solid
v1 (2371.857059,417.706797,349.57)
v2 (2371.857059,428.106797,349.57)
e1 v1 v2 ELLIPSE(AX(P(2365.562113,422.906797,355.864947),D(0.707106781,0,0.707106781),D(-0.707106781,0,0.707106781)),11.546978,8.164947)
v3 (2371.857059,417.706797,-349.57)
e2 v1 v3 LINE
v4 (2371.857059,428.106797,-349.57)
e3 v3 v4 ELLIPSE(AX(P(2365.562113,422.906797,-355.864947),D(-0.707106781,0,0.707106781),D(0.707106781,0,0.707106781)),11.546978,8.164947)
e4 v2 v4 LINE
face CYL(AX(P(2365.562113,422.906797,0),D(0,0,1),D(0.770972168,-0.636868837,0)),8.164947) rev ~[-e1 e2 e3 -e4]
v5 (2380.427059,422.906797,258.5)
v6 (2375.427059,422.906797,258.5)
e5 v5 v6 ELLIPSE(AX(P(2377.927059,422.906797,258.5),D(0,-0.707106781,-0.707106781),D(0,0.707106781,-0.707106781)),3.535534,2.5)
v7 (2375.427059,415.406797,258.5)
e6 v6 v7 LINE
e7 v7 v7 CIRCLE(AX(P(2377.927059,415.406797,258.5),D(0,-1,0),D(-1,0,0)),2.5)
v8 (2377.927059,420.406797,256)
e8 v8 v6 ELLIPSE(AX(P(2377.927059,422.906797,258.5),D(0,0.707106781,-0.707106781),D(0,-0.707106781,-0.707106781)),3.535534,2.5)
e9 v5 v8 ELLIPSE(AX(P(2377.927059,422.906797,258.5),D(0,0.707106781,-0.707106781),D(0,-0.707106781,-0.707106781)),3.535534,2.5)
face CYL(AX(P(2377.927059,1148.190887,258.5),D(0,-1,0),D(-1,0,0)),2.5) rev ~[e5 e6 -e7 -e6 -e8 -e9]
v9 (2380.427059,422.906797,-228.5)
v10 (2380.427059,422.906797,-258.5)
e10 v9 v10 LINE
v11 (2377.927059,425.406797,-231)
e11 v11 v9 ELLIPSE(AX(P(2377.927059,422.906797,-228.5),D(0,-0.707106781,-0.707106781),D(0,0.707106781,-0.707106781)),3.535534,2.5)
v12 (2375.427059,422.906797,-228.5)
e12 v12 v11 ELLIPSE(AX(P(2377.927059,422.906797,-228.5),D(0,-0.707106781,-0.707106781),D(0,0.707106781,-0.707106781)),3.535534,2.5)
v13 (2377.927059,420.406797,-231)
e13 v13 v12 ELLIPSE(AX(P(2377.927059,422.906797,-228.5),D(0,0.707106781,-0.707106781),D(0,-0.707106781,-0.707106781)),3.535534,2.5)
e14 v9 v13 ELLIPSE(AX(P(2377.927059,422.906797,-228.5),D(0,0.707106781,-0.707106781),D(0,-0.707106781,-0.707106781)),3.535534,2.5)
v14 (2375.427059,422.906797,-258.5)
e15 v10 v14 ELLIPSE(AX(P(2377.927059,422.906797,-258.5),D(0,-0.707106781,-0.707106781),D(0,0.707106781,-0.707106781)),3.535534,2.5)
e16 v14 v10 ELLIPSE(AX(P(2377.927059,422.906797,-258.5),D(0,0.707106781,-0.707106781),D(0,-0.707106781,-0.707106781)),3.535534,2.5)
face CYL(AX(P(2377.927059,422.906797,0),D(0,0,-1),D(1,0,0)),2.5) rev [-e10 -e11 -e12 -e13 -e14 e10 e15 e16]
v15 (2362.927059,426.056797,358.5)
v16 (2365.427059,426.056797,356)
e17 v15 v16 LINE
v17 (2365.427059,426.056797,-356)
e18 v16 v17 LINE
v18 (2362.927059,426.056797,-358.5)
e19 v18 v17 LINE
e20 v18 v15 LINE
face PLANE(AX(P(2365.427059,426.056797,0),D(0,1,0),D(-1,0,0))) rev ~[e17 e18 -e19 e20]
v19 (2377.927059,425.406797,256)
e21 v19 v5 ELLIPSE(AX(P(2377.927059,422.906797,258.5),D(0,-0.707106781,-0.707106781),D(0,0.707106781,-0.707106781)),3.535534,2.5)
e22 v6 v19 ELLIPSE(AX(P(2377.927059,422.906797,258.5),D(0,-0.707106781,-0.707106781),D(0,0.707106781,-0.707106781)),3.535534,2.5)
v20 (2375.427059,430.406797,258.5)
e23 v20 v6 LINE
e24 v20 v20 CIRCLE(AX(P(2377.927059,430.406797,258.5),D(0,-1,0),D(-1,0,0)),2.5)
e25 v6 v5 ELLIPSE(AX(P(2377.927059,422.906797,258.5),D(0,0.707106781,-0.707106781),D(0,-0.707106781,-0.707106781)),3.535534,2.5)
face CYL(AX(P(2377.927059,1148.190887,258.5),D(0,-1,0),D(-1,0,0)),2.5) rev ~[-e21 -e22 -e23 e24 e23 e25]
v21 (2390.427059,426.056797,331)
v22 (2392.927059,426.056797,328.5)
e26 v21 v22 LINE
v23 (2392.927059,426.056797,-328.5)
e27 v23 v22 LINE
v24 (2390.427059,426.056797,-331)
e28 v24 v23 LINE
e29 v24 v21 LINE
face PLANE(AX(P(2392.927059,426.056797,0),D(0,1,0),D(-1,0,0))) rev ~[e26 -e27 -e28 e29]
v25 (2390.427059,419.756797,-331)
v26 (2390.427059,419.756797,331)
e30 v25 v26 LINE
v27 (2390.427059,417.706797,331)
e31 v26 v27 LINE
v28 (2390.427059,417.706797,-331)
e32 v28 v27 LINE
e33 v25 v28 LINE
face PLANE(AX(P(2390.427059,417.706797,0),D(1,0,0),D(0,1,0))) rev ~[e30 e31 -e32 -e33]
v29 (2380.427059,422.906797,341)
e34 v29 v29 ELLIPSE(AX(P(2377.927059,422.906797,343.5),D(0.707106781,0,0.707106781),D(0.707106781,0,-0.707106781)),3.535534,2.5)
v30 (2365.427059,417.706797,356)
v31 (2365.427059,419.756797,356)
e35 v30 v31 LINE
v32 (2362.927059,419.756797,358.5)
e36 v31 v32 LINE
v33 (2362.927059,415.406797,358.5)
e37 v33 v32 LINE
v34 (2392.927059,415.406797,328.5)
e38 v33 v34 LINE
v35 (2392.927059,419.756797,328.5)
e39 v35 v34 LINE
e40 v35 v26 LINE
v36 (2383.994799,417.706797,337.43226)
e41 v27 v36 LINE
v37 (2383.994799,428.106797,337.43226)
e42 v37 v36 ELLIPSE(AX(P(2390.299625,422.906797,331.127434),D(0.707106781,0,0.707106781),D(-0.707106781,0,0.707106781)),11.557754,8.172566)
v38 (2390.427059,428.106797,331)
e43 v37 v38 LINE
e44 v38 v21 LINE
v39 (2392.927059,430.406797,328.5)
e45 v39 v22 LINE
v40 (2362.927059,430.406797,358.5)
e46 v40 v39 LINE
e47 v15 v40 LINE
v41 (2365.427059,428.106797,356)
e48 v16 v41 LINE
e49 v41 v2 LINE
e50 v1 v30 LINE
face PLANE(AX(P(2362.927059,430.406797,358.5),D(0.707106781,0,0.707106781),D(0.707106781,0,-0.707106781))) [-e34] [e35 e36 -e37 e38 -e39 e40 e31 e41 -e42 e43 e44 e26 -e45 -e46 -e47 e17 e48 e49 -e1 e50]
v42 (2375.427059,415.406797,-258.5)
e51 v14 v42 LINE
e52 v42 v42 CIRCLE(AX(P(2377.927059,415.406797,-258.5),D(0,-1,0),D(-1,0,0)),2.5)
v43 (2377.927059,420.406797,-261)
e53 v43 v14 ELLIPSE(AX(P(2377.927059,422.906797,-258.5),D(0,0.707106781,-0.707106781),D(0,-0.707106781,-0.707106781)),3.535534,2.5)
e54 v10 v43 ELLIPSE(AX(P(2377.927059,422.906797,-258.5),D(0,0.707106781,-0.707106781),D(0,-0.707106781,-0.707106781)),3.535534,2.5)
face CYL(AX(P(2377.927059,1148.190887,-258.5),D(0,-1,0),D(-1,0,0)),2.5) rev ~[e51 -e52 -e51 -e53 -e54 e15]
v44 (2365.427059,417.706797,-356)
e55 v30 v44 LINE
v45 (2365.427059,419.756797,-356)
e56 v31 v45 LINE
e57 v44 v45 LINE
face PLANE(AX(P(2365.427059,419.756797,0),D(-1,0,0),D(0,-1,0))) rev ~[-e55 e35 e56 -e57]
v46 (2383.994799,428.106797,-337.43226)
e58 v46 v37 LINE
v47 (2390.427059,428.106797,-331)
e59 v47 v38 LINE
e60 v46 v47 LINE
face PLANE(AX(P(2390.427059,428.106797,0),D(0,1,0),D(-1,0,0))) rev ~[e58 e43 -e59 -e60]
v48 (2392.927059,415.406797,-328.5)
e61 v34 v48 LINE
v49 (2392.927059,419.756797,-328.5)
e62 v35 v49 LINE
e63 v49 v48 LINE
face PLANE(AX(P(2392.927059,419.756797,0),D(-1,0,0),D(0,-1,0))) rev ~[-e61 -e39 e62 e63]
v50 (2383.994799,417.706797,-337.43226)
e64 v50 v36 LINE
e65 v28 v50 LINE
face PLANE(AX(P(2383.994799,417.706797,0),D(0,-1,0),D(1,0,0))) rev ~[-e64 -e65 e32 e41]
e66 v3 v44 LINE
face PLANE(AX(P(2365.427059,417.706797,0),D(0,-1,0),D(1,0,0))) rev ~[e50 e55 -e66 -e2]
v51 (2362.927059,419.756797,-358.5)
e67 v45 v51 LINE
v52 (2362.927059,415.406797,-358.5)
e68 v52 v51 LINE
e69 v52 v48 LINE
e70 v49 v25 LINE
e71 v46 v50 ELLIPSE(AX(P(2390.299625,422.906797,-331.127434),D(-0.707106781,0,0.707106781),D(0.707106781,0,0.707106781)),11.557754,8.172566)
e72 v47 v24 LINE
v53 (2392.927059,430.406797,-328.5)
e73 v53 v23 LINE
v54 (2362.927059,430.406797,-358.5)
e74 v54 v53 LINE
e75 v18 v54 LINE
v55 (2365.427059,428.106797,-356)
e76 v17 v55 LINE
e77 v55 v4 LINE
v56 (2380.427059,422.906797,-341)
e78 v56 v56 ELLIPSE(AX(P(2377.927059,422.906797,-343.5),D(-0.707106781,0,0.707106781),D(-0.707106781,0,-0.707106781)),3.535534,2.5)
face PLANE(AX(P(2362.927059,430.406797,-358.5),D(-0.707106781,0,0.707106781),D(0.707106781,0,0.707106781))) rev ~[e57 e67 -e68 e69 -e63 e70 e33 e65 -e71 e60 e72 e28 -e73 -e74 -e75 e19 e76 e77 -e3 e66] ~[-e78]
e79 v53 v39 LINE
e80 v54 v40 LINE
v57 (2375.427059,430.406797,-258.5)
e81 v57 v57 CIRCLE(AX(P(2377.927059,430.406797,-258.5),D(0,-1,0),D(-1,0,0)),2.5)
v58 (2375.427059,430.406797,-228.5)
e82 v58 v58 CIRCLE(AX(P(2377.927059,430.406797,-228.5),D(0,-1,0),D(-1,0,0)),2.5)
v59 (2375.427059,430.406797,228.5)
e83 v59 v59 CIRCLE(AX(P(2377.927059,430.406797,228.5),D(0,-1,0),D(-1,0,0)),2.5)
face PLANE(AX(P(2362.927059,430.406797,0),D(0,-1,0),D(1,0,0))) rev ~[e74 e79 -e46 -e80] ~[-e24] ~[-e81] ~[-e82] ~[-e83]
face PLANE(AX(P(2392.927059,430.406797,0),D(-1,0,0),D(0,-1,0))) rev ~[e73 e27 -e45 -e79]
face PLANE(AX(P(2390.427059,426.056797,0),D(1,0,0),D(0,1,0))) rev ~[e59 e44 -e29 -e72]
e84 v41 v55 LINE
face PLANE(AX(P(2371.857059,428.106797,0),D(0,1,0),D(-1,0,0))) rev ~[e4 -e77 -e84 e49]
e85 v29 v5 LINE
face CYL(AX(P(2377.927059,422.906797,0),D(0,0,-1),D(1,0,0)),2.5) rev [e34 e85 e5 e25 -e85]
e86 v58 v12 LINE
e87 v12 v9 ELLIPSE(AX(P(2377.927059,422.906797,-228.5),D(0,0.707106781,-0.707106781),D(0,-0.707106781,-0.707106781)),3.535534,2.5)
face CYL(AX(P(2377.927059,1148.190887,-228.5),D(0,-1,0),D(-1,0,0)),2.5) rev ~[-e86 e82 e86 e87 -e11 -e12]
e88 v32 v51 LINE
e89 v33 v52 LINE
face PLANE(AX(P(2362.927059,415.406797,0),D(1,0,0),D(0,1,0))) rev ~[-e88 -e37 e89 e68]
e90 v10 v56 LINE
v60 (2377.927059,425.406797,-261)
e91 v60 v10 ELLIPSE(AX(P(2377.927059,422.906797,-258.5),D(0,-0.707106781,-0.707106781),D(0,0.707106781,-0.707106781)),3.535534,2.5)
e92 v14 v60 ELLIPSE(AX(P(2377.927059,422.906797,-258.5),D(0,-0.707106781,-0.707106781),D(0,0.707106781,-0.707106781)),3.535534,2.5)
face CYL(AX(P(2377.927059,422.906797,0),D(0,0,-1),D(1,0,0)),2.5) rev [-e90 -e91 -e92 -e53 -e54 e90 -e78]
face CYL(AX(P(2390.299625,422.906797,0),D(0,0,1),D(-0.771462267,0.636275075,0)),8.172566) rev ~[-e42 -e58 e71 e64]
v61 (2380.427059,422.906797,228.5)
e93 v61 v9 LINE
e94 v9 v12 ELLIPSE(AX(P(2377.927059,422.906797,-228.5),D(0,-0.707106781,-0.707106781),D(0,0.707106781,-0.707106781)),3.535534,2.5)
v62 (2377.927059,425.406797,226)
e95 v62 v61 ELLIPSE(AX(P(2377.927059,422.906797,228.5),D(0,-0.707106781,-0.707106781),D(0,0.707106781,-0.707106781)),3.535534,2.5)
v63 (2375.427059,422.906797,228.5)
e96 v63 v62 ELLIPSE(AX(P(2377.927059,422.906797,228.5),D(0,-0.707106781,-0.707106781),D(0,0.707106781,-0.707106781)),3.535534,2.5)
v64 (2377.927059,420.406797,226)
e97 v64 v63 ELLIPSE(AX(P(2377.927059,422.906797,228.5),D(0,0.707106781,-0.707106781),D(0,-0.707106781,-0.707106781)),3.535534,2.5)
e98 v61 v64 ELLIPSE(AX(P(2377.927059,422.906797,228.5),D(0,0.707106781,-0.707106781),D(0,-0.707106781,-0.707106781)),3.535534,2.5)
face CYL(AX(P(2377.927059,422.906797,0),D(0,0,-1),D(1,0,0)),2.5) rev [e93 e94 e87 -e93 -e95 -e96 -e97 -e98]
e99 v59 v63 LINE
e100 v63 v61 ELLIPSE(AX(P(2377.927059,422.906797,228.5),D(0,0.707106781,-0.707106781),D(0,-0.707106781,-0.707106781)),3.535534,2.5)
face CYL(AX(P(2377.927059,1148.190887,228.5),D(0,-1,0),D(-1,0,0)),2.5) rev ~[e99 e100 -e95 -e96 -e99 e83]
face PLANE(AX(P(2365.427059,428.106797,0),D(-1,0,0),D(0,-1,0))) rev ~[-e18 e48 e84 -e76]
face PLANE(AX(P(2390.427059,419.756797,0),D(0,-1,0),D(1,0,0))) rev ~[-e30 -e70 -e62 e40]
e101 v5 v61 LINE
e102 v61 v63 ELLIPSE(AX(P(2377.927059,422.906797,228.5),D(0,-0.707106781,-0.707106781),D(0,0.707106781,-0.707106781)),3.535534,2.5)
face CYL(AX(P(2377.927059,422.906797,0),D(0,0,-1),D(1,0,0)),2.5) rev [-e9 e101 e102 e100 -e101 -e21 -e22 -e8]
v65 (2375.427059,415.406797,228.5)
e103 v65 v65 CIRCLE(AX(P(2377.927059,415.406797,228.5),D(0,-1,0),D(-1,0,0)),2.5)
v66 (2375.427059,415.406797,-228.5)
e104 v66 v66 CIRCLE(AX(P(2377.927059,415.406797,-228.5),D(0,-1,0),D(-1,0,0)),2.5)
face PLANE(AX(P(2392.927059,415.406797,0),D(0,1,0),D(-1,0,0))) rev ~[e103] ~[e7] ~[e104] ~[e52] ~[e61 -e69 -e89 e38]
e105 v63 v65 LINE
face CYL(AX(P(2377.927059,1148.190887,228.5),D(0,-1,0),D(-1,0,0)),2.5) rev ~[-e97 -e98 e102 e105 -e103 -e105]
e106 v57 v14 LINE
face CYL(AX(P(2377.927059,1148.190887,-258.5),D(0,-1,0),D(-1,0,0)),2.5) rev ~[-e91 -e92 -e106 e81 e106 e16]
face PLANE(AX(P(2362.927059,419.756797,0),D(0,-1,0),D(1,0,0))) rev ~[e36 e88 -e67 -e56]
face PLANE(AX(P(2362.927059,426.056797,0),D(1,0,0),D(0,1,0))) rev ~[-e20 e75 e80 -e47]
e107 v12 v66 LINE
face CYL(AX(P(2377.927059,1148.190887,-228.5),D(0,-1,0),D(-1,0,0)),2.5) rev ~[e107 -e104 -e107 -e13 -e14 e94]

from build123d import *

# Parameters (mm, degrees)
MODEL_R             = 2.5
EXTRUDE_1_DEPTH     = 358.5
CUT_EXTRUDE_1_DEPTH = 2420.679144403
HOLE_WIZARD_M6_1_D  = 5


with BuildPart() as part:
    # Model → 凸台-拉伸1 (new, symmetric)
    with BuildSketch(Plane.XY):
        with BuildLine():
            Line((2390.427059452, 419.756797217), (2392.927059452, 419.756797217))
            Line((2392.927059452, 419.756797217), (2392.927059452, 415.406797217))
            Line((2392.927059452, 415.406797217), (2362.927059452, 415.406797217))
            Line((2362.927059452, 415.406797217), (2362.927059452, 419.756797217))
            Line((2362.927059452, 419.756797217), (2365.427059452, 419.756797217))
            Line((2365.427059452, 419.756797217), (2365.427059452, 417.706797217))
            Line((2365.427059452, 417.706797217), (2371.857059452, 417.706797217))
            ThreePointArc((2371.857059452, 417.706797217), (2373.727059452, 422.906797217), (2371.857059452, 428.106797217))
            Line((2371.857059452, 428.106797217), (2365.427059452, 428.106797217))
            Line((2365.427059452, 428.106797217), (2365.427059452, 426.056797217))
            Line((2365.427059452, 426.056797217), (2362.927059452, 426.056797217))
            Line((2362.927059452, 426.056797217), (2362.927059452, 430.406797217))
            Line((2362.927059452, 430.406797217), (2392.927059452, 430.406797217))
            Line((2392.927059452, 430.406797217), (2392.927059452, 426.056797217))
            Line((2392.927059452, 426.056797217), (2390.427059452, 426.056797217))
            Line((2390.427059452, 426.056797217), (2390.427059452, 428.106797217))
            Line((2390.427059452, 428.106797217), (2383.994799144, 428.106797217))
            ThreePointArc((2383.994799144, 428.106797217), (2382.127059452, 422.906797217), (2383.994799144, 417.706797217))
            Line((2383.994799144, 417.706797217), (2390.427059452, 417.706797217))
            Line((2390.427059452, 417.706797217), (2390.427059452, 419.756797217))
        make_face()
        with Locations((2377.927059452, 422.906797217)):
            Circle(MODEL_R, mode=Mode.SUBTRACT)
    extrude(amount=EXTRUDE_1_DEPTH, both=True)

    # 草图1 → 切除-拉伸1 (cut, through all)
    with BuildSketch(Plane(origin=(0, 430.406797217, 0), x_dir=(1, 0, 0), z_dir=(0, 1, 0))):
        Polygon((2362.927059452, 358.5), (2392.927059452, 328.5), (2392.927059452, 358.5), align=None)
        Polygon((2362.927059452, -358.5), (2392.927059452, -328.5), (2392.927059452, -358.5), align=None)
    extrude(amount=-CUT_EXTRUDE_1_DEPTH, mode=Mode.SUBTRACT)

    # M6 螺纹孔1 (through all)
    with Locations(Plane(origin=(0, 430.406797217, 0), x_dir=(1, 0, 0), z_dir=(0, 1, 0))):
        with Locations((2377.927059452, -258.5), (2377.927059452, -228.5), (2377.927059452, 228.5), (2377.927059452, 258.5)):
            Hole(HOLE_WIZARD_M6_1_D / 2)


solid = part.part
